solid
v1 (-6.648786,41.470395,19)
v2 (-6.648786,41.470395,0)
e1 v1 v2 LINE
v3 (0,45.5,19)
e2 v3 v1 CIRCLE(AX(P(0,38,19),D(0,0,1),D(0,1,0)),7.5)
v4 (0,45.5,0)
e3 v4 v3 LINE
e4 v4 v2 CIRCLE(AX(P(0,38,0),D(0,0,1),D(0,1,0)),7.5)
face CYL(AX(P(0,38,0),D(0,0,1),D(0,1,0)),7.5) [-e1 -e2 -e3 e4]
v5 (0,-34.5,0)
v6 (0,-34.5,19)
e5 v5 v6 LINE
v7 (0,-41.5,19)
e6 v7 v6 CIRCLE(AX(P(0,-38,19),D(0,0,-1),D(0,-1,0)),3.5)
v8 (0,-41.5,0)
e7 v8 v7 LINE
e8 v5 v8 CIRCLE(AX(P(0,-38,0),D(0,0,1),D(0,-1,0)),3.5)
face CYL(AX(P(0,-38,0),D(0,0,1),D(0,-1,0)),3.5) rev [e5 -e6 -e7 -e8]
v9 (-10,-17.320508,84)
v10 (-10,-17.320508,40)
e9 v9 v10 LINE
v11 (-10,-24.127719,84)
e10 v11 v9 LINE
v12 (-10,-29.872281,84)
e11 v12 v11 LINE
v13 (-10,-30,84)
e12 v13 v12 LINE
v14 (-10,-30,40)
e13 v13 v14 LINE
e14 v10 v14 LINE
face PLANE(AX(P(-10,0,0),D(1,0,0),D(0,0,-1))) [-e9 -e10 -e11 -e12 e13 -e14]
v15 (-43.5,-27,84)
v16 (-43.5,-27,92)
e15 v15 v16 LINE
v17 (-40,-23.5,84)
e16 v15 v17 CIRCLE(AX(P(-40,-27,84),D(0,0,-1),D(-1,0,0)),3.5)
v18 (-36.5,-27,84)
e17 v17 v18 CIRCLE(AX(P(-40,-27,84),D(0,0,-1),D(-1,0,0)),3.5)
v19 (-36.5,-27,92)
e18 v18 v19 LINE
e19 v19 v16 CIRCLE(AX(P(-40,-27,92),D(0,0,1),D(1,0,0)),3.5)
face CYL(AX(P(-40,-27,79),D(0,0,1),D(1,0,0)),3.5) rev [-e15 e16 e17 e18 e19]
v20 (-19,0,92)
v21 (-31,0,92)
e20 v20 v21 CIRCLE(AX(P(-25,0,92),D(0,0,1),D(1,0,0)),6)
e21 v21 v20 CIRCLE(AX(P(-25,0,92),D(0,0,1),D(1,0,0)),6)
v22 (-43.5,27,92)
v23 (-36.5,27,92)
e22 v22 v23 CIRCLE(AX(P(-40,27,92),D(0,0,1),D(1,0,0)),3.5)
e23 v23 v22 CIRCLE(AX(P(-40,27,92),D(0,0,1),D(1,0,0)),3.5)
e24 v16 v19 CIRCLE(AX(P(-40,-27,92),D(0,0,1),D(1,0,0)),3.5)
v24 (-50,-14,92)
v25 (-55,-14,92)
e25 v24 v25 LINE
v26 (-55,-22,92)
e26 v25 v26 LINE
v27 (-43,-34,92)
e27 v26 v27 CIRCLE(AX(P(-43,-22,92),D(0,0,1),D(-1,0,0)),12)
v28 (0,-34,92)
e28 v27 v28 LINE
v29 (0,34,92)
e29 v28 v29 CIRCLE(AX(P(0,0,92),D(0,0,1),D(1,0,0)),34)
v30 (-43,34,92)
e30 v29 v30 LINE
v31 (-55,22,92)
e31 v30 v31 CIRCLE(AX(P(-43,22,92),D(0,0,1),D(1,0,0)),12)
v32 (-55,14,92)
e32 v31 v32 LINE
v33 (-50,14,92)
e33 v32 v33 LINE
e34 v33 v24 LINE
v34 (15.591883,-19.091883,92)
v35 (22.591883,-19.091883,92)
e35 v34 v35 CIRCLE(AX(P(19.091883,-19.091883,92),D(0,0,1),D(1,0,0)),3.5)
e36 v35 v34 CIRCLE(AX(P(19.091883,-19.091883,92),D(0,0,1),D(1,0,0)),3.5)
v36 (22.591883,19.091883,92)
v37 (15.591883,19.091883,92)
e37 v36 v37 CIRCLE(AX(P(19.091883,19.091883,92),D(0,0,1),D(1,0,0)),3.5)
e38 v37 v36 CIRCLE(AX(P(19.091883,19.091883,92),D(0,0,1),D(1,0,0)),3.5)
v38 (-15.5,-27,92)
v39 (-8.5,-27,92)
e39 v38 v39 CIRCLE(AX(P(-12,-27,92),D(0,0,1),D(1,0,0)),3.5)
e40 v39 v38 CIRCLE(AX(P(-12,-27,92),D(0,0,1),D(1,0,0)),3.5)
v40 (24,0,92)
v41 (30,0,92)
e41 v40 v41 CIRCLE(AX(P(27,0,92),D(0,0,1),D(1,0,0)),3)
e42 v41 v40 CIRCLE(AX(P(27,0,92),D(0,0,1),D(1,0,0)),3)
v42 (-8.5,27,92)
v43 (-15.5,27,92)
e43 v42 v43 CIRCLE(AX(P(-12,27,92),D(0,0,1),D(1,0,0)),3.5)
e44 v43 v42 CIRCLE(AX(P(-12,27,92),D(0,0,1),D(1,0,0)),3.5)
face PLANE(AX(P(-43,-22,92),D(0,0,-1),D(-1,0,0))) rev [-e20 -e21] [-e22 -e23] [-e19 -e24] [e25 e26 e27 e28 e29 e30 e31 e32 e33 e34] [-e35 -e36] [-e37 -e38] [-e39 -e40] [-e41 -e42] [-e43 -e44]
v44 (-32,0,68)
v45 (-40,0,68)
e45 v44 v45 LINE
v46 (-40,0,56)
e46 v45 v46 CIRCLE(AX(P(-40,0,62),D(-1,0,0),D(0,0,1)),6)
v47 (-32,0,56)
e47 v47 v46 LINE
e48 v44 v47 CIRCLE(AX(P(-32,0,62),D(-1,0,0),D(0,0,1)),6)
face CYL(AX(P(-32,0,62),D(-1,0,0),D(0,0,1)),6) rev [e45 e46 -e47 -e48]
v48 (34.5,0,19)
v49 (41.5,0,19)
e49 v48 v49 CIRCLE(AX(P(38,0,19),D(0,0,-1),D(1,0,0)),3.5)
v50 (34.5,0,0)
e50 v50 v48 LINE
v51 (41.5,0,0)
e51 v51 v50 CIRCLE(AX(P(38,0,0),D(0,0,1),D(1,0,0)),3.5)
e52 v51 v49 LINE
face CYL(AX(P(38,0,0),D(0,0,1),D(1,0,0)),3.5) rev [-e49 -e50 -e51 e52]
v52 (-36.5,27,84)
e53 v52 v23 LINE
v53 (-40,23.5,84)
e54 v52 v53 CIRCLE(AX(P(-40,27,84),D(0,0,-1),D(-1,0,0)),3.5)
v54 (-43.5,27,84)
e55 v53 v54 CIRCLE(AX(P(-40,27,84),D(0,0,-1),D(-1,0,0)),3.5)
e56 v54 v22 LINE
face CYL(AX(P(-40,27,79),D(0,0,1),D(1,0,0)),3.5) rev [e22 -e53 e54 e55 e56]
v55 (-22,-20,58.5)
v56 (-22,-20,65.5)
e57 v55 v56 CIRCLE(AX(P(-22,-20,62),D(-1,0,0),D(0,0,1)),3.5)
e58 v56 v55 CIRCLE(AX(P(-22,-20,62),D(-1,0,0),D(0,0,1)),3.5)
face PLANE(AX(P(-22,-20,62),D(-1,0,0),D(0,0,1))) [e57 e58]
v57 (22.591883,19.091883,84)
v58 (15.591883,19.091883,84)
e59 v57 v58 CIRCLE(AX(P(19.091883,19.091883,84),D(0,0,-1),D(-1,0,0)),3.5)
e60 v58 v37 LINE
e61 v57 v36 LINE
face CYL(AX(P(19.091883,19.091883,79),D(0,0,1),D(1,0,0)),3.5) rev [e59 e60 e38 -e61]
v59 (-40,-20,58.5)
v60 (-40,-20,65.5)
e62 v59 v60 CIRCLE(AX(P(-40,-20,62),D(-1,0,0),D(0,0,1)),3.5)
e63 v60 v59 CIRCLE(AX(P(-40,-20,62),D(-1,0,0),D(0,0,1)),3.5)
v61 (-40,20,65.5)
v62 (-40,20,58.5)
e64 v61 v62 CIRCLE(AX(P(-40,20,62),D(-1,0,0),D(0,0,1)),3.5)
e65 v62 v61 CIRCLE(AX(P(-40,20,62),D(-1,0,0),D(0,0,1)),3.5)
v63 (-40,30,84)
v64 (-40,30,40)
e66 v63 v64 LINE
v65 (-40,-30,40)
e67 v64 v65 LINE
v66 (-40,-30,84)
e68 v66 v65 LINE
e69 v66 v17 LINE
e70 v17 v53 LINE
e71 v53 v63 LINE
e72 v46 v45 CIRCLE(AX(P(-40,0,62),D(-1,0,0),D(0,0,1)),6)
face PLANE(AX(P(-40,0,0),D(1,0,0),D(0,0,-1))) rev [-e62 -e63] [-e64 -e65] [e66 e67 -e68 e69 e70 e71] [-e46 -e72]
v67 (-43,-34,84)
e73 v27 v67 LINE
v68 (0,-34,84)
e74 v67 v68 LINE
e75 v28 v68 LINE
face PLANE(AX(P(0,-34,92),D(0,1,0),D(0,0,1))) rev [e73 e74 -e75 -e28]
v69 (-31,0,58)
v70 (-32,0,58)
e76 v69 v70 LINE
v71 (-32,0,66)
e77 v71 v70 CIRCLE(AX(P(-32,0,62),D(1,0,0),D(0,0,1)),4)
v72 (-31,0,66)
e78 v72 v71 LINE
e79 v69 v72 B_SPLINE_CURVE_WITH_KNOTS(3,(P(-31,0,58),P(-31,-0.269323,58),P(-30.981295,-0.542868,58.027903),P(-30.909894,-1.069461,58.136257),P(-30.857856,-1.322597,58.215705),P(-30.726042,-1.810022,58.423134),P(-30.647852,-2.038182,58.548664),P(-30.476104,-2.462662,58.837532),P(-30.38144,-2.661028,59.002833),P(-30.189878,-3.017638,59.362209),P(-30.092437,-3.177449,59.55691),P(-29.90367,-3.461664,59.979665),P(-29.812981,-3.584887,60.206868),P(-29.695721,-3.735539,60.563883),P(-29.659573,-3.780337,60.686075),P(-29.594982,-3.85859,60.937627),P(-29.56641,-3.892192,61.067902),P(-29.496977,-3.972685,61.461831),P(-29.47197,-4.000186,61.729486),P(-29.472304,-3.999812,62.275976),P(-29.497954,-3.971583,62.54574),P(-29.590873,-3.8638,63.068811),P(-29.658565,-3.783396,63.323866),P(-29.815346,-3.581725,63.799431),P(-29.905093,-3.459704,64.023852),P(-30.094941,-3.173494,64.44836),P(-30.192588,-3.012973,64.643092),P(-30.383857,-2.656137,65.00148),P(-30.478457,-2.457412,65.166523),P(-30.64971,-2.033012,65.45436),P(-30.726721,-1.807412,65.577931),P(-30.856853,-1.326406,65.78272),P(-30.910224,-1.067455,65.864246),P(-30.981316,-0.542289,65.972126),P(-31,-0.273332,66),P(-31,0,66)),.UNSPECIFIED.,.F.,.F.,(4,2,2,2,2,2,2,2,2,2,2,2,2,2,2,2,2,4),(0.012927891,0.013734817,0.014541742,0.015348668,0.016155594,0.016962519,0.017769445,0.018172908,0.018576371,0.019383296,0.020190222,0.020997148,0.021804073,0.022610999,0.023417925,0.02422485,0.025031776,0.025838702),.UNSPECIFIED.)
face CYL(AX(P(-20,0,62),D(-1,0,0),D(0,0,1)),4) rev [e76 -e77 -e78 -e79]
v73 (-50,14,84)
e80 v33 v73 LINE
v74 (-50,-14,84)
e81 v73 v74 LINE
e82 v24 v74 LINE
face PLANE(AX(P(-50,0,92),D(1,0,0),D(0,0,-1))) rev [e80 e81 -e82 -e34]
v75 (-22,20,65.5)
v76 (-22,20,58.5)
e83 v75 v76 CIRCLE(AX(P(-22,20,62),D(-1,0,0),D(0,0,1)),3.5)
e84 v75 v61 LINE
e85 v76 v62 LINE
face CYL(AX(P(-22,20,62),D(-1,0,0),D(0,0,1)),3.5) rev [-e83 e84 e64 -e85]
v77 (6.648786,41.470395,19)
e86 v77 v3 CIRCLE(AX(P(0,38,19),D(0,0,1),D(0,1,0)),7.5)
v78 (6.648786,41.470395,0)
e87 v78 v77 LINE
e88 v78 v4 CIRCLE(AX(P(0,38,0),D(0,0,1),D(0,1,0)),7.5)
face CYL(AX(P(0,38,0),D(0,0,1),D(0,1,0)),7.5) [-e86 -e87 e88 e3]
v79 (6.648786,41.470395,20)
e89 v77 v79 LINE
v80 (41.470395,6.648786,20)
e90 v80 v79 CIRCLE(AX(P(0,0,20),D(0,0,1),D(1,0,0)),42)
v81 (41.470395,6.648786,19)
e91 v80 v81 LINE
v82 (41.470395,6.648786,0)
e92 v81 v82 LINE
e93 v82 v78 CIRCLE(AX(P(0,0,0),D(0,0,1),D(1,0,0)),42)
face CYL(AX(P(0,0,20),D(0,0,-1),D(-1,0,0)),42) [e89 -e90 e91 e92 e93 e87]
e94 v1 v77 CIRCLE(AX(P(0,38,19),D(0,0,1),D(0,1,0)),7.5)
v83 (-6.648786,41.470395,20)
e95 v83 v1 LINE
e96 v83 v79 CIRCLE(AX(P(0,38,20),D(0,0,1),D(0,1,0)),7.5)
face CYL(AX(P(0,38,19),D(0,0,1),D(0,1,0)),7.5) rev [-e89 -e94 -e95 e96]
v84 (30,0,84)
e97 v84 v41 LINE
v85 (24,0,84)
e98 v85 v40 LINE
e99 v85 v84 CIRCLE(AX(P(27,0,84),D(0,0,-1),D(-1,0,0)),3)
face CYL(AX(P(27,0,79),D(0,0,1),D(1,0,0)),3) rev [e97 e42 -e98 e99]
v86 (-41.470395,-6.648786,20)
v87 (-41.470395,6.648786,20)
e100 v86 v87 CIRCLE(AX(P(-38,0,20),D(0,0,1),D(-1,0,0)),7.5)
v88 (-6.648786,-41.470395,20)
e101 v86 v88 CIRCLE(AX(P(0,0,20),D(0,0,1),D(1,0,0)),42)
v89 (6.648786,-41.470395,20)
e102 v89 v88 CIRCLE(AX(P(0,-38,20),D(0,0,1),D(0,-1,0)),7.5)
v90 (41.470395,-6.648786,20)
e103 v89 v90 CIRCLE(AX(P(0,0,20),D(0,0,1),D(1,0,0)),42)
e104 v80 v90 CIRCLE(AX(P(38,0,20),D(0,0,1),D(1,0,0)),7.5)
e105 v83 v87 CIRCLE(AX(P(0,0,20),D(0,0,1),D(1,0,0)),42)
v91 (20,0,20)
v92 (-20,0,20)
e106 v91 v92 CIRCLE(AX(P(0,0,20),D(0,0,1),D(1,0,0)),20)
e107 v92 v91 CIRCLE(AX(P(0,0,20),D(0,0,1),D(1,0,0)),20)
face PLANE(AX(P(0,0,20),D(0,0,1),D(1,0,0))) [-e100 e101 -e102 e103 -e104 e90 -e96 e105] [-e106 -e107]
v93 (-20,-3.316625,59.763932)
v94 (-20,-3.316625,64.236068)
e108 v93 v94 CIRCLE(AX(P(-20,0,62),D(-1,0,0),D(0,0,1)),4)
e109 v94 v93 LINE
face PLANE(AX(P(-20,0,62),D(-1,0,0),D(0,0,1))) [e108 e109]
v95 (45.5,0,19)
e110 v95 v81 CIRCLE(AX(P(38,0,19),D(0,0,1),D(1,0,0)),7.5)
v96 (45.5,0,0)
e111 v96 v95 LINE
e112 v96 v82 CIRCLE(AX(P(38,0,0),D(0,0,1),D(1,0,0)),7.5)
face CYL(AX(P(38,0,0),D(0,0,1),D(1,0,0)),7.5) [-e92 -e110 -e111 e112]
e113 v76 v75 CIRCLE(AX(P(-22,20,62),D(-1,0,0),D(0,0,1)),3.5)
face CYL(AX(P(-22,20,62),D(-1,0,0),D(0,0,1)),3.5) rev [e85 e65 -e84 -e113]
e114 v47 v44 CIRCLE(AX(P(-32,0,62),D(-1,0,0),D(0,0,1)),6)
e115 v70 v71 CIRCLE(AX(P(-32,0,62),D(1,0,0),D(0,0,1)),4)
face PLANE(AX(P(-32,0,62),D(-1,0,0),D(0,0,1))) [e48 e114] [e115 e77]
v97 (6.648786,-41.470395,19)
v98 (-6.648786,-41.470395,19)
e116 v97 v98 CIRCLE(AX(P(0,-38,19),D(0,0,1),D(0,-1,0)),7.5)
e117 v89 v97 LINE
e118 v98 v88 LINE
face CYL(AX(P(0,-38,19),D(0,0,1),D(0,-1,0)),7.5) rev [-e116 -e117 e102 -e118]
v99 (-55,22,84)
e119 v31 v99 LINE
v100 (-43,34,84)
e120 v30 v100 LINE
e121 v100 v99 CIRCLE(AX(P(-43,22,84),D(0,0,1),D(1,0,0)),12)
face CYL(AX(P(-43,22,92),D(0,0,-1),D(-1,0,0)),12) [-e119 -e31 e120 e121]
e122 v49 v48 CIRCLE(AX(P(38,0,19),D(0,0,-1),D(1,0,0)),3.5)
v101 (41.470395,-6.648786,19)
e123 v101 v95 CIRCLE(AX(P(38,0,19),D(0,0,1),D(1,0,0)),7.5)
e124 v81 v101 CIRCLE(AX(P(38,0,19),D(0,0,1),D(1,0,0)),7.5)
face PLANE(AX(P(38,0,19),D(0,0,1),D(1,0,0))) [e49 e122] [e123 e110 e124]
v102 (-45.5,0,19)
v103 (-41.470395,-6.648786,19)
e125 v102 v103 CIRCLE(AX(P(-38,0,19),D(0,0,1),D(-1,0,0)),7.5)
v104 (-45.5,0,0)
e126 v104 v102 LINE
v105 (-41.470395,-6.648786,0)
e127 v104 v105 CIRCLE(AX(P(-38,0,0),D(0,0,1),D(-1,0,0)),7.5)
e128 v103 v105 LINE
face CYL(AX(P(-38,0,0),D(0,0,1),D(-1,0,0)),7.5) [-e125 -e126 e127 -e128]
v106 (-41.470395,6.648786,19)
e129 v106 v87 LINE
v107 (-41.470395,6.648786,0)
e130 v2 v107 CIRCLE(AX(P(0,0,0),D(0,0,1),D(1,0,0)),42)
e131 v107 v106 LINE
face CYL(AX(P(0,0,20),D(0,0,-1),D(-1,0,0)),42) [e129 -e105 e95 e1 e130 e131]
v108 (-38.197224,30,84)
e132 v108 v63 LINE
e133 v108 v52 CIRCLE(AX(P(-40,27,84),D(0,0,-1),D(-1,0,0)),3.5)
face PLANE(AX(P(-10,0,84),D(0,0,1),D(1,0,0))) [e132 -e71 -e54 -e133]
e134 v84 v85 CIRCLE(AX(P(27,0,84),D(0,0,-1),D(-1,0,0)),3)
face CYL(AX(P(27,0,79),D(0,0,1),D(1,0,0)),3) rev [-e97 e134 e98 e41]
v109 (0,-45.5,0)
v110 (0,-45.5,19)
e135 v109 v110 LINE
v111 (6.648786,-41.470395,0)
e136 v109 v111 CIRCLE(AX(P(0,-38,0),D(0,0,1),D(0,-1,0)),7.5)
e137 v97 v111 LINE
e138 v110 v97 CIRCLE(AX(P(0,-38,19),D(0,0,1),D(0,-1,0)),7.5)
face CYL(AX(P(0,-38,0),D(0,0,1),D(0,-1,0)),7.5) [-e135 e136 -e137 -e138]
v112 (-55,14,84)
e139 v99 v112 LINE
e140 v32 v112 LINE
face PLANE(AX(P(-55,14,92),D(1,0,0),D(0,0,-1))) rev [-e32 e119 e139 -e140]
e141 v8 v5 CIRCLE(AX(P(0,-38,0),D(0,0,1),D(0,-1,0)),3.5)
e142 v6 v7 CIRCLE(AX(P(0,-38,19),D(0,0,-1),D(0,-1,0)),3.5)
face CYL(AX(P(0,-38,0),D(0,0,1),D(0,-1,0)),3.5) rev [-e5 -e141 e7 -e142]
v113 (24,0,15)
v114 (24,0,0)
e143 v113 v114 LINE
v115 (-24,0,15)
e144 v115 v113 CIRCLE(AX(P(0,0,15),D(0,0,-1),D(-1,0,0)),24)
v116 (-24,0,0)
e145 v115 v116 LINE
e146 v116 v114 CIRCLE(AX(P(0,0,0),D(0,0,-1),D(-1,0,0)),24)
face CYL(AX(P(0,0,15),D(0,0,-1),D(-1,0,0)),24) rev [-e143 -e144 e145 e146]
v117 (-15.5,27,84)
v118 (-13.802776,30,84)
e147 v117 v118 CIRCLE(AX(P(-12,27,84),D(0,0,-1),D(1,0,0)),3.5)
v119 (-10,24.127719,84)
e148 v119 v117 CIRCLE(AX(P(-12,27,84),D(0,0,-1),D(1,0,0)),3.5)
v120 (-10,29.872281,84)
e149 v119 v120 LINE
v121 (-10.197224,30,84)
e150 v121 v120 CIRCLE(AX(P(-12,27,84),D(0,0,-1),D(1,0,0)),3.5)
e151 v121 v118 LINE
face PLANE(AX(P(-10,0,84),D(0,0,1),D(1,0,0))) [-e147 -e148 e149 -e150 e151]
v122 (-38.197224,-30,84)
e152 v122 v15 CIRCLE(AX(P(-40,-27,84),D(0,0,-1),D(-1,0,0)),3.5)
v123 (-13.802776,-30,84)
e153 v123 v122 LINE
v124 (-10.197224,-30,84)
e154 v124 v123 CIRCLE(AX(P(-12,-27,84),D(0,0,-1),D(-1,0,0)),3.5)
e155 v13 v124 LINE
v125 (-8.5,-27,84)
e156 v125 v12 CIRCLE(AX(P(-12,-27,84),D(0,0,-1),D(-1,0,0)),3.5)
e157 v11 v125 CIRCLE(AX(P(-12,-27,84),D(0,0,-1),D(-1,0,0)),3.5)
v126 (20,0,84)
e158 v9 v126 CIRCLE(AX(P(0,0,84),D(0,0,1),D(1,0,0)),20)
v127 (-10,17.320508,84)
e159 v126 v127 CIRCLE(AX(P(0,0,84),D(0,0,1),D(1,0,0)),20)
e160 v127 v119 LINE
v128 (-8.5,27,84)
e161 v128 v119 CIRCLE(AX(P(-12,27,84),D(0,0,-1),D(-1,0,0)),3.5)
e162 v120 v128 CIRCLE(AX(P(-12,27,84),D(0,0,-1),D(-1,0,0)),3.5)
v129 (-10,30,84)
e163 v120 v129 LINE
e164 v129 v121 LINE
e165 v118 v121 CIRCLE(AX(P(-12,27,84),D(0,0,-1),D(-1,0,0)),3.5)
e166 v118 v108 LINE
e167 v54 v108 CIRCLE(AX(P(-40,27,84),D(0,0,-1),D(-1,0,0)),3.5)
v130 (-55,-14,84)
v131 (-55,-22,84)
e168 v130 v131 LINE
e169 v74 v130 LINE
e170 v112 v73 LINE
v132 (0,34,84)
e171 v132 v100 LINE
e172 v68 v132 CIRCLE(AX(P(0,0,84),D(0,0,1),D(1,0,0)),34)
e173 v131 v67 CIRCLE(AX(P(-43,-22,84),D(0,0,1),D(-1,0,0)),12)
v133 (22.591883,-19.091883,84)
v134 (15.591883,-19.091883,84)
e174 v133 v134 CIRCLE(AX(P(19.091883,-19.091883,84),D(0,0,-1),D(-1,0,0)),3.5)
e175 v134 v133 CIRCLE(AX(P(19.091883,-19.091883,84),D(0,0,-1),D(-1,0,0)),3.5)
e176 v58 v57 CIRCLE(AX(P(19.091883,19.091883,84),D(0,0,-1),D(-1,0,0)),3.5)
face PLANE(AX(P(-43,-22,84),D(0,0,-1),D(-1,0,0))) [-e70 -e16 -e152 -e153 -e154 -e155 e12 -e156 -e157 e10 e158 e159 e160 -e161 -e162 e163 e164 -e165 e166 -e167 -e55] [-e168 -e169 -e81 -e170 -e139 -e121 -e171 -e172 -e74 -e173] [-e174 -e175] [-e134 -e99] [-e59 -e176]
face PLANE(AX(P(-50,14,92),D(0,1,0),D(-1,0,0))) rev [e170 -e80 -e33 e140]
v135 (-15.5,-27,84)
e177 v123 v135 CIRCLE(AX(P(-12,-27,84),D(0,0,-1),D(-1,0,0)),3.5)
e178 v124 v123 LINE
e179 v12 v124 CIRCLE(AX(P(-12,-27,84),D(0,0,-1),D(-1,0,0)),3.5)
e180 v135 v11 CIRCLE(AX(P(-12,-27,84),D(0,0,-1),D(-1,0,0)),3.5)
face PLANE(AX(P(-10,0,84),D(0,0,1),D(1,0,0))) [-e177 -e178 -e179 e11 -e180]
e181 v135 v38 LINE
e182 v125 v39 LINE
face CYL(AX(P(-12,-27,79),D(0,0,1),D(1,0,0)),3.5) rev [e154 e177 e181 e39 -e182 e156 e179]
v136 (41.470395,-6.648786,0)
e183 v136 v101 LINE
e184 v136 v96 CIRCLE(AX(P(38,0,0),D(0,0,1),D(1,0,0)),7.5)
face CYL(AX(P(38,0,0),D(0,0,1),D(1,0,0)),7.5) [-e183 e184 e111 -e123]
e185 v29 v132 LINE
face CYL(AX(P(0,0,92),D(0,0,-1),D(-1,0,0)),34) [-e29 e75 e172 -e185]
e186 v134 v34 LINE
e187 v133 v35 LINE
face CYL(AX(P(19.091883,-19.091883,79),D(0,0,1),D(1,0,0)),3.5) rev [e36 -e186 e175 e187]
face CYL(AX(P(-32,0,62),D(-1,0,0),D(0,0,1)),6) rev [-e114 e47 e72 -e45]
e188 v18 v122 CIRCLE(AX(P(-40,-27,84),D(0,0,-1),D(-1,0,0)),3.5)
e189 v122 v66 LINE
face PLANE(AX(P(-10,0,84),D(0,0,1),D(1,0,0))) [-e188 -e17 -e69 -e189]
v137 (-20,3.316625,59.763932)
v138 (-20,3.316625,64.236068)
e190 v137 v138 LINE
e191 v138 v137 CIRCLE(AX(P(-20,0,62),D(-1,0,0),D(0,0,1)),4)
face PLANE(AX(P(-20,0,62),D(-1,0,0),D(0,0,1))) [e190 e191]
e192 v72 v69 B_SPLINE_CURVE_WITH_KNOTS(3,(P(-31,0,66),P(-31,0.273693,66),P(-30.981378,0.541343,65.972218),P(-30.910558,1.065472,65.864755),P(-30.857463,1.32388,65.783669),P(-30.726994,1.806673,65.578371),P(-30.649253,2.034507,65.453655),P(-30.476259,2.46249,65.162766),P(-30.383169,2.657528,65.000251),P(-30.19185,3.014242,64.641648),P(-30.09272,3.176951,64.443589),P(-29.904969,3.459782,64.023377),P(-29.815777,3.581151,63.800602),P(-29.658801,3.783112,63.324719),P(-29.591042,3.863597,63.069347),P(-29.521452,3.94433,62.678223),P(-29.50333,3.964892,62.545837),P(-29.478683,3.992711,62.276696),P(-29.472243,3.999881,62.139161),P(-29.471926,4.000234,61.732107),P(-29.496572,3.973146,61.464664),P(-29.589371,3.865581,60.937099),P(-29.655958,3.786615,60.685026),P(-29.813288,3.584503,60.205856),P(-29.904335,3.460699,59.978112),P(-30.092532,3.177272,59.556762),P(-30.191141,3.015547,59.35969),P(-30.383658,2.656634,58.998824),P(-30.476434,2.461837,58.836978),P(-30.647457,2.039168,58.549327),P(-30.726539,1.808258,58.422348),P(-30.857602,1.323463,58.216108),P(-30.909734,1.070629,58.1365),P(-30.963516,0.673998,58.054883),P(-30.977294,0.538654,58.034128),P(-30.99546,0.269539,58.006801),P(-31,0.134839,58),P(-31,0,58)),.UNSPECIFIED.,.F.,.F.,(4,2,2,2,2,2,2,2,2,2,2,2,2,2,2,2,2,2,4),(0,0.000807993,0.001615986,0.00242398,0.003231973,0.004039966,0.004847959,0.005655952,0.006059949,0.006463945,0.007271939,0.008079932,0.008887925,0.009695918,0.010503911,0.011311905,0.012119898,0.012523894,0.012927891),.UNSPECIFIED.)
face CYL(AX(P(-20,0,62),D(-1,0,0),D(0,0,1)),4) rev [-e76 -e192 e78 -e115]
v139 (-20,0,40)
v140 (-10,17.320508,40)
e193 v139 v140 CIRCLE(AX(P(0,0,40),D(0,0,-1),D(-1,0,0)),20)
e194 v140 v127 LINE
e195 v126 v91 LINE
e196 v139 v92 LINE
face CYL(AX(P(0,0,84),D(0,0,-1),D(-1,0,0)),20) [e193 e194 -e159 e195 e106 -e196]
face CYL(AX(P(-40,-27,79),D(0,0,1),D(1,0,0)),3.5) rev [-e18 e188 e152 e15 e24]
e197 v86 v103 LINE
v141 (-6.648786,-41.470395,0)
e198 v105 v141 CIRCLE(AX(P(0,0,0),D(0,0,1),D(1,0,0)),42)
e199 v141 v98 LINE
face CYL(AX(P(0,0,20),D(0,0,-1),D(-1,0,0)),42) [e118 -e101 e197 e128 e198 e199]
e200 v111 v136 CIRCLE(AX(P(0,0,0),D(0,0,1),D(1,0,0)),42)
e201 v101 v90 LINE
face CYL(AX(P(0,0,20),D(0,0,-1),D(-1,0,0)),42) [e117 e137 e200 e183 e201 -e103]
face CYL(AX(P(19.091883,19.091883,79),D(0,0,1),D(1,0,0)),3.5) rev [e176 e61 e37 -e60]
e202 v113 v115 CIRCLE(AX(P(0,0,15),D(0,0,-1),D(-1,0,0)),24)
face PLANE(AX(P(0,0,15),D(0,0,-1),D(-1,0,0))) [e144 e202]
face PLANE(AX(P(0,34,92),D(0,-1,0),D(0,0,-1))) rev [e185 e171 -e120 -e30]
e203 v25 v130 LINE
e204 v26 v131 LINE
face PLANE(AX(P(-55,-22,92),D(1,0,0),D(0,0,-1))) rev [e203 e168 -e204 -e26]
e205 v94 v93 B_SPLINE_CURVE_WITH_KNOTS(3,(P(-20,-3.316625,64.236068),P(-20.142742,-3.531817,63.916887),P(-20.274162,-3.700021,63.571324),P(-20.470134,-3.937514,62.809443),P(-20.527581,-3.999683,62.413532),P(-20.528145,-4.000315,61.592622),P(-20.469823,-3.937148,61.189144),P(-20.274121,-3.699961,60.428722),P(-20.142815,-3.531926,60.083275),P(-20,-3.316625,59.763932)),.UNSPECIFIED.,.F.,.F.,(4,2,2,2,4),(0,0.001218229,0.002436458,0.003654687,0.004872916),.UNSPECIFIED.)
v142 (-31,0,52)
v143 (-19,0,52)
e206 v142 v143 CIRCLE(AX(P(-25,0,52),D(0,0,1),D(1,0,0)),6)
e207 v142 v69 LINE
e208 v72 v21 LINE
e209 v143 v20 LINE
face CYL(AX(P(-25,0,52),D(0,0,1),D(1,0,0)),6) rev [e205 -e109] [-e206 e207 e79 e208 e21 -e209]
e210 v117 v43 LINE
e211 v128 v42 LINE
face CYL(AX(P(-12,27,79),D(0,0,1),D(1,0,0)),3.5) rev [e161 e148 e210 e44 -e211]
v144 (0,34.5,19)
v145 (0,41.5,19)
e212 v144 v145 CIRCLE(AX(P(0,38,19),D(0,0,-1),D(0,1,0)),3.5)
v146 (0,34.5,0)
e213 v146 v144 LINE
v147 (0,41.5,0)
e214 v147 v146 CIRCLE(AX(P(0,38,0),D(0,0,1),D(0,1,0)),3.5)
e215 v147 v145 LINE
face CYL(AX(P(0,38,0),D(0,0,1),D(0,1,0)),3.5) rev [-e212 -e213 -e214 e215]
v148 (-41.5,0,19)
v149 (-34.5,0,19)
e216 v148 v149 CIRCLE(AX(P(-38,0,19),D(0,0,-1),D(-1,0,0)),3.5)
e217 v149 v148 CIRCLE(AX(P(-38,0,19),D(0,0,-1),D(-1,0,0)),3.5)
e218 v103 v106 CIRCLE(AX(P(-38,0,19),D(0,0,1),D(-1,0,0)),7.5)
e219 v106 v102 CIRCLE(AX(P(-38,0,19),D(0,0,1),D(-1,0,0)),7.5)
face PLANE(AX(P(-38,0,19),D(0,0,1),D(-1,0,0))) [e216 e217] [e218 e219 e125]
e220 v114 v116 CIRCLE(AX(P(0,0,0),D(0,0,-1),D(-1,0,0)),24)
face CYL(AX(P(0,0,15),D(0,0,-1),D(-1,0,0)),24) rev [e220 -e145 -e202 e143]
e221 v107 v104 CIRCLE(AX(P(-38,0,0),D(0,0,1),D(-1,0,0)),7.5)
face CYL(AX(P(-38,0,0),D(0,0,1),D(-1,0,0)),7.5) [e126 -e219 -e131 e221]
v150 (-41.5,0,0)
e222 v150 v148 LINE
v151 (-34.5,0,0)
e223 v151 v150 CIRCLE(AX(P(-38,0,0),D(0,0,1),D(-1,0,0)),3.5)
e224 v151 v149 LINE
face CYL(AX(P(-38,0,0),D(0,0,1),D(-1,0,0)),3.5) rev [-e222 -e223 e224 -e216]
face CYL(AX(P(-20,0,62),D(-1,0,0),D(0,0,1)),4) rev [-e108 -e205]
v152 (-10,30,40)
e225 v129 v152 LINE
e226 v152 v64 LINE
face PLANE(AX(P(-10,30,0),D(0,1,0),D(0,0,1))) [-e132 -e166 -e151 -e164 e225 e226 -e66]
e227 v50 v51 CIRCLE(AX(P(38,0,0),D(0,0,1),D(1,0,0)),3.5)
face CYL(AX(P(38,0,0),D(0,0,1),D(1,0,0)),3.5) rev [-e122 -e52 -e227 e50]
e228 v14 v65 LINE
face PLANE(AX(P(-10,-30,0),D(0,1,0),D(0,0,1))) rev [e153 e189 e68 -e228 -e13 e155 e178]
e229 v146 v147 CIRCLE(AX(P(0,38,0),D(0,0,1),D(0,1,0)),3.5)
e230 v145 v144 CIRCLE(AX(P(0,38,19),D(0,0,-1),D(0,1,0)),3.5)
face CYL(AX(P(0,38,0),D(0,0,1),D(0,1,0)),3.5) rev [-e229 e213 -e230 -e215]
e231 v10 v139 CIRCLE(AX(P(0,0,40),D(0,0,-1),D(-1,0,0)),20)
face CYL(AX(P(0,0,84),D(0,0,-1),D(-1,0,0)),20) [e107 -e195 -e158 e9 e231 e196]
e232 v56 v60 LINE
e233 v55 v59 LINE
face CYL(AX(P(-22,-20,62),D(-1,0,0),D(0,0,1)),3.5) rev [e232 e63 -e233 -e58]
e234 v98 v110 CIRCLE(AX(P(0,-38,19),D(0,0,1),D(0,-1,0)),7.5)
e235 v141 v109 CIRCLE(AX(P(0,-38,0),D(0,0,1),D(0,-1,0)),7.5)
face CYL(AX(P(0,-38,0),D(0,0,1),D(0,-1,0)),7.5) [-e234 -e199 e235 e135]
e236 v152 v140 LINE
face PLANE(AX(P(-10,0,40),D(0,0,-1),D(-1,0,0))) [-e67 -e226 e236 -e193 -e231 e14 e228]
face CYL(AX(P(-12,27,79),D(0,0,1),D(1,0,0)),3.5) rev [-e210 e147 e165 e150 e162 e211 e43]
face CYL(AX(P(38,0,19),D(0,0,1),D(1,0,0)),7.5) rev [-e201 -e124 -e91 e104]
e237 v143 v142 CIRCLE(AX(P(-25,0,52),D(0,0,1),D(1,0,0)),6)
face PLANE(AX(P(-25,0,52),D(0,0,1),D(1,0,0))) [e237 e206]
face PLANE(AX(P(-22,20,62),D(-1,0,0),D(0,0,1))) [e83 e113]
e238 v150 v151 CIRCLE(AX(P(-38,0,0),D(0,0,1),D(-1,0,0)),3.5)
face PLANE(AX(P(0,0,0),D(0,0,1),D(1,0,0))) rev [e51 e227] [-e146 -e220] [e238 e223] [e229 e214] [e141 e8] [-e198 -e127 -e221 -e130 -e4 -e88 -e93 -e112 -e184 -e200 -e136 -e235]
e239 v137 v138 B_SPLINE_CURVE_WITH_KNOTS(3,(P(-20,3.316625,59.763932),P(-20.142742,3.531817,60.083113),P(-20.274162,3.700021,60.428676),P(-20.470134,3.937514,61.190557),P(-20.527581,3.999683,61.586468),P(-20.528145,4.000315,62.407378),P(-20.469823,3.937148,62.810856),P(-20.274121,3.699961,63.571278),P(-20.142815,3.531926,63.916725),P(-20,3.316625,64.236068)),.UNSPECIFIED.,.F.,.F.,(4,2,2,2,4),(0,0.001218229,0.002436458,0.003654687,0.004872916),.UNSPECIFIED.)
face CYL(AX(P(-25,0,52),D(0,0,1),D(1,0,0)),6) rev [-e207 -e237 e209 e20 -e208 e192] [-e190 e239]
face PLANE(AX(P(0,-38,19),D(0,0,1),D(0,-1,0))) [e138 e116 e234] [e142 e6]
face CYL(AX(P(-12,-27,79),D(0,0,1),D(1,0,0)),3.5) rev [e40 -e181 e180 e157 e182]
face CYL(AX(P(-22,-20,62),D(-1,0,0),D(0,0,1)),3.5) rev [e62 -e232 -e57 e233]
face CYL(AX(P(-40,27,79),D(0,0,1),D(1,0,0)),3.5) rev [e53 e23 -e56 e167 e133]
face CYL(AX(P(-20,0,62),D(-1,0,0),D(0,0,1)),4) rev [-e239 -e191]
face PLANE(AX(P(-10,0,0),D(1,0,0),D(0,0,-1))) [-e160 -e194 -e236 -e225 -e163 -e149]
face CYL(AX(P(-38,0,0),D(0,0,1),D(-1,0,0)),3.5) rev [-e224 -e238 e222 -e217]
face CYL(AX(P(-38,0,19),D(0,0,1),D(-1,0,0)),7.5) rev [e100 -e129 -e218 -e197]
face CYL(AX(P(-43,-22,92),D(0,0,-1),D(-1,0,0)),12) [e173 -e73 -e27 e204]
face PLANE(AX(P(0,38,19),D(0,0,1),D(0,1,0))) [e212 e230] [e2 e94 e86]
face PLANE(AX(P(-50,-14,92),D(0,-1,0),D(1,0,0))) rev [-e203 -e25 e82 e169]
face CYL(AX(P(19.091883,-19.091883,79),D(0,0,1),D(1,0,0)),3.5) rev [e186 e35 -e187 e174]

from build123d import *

# Parameters (mm, degrees)
REAR_FLANGE_SKETCH_84_R         = 42
REAR_FLANGE_84_DEPTH            = 20
BODY_CYLINDER_SKETCH_40_R       = 20
BODY_CYLINDER_40_DEPTH          = 64
FRONT_PLATE_DEPTH               = 8
FRONT_PLATE_SIDE_NOTCH_SKETCH_R = 2.5
FRONT_PLATE_SIDE_NOTCH_DEPTH    = 16
NOTCH_HOLE_SKETCH_6_R           = 3
NOTCH_HOLE_6_DEPTH              = 13
FRONT_PLATE_HOLES_SKETCH_R      = 3.5
FRONT_PLATE_HOLES_7_DEPTH       = 13
TOP_BLOCK_DEPTH                 = 30
FRONT_CENTER_BORE_SKETCH_R      = 6
FRONT_CENTER_BORE_DEPTH         = 40
TOP_BLOCK_POCKET_SKETCH_R       = 4
TOP_BLOCK_POCKET_DEPTH          = 20
TOP_BLOCK_HOLE_SKETCH_12_R      = 6
TOP_BLOCK_HOLE_12_DEPTH         = 8
TOP_BLOCK_SLOT_SKETCH_R         = 3.5
TOP_BLOCK_SLOT_DEPTH            = 18
REAR_HUB_SKETCH_40_R            = 20
REAR_HUB_40_DEPTH               = 11
FLANGE_PROFILE_TRIM_SKETCH_R    = 3.5
FLANGE_PROFILE_TRIM_DEPTH       = 100.864908824
FLANGE_LUG_SKETCH_15_R          = 7.5
FLANGE_LUG_15_DEPTH             = 20
LUG_HOLE_SKETCH_7_R             = 3.5
LUG_HOLE_7_DEPTH                = 100.864908824
LUG_RECESS_SKETCH_R             = 7.5
LUG_RECESS_1MM_DEPTH            = 1
REAR_COUNTERBORE_SKETCH_48_R    = 24
REAR_COUNTERBORE_48_DEPTH       = 15
FLANGE_LUG_PATTERN_4X_COUNT     = 4


with BuildPart() as part:
    # Rear Flange Sketch Ø84 → Rear Flange Ø84 (new body)
    with BuildSketch(Plane.XY):
        Circle(REAR_FLANGE_SKETCH_84_R)
    extrude(amount=REAR_FLANGE_84_DEPTH)

    # Body Cylinder Sketch Ø40 → Body Cylinder Ø40 (add)
    with BuildSketch(Plane.XY.offset(20)):
        Circle(BODY_CYLINDER_SKETCH_40_R)
    extrude(amount=BODY_CYLINDER_40_DEPTH)

    # Front Plate Sketch → Front Plate (add)
    with BuildSketch(Plane.XY.offset(84)):
        with BuildLine():
            Line((0, 34), (-43, 34))
            ThreePointArc((-43, 34), (-51.485281374, 30.485281374), (-55, 22))
            Line((-55, 22), (-55, 14))
            Line((-55, 14), (-50, 14))
            Line((-50, 14), (-50, 0))
            Line((-50, 0), (-50, -14))
            Line((-50, -14), (-55, -14))
            Line((-55, -14), (-55, -22))
            ThreePointArc((-55, -22), (-51.485281374, -30.485281374), (-43, -34))
            Line((-43, -34), (0, -34))
            ThreePointArc((0, -34), (34, 0), (0, 34))
        make_face()
    extrude(amount=FRONT_PLATE_DEPTH)

    # Front Plate Side Notch Sketch → Front Plate Side Notch (cut)
    with BuildSketch(Plane.XY.offset(92)):
        with Locations((27, 0)):
            Circle(FRONT_PLATE_SIDE_NOTCH_SKETCH_R)
    extrude(amount=-FRONT_PLATE_SIDE_NOTCH_DEPTH, mode=Mode.SUBTRACT)

    # Notch Hole Sketch Ø6 → Notch Hole Ø6 (cut)
    with BuildSketch(Plane.XY.offset(92)):
        with Locations((27, 0)):
            Circle(NOTCH_HOLE_SKETCH_6_R)
    extrude(amount=-NOTCH_HOLE_6_DEPTH, mode=Mode.SUBTRACT)

    # Front Plate Holes Sketch → Front Plate Holes Ø7 (cut)
    with BuildSketch(Plane.XY.offset(92)):
        with Locations((19.091883092, 19.091883092)):
            Circle(FRONT_PLATE_HOLES_SKETCH_R)
        with Locations((19.091883092, -19.091883092)):
            Circle(FRONT_PLATE_HOLES_SKETCH_R)
        with Locations((-12, 27)):
            Circle(FRONT_PLATE_HOLES_SKETCH_R)
        with Locations((-40, 27)):
            Circle(FRONT_PLATE_HOLES_SKETCH_R)
        with Locations((-12, -27)):
            Circle(FRONT_PLATE_HOLES_SKETCH_R)
        with Locations((-40, -27)):
            Circle(FRONT_PLATE_HOLES_SKETCH_R)
    extrude(amount=-FRONT_PLATE_HOLES_7_DEPTH, mode=Mode.SUBTRACT)

    # Top Block Sketch → Top Block (add)
    with BuildSketch(Plane(origin=(-40, 0, 0), x_dir=(0, 0, -1), z_dir=(1, 0, 0))):
        Polygon((-84, 30), (-84, 0), (-84, -30), (-40, -30), (-40, 0), (-40, 30), align=None)
    extrude(amount=TOP_BLOCK_DEPTH)

    # Front Center Bore Sketch → Front Center Bore (cut)
    with BuildSketch(Plane.XY.offset(92)):
        with Locations((-25, 0)):
            Circle(FRONT_CENTER_BORE_SKETCH_R)
    extrude(amount=-FRONT_CENTER_BORE_DEPTH, mode=Mode.SUBTRACT)

    # Top Block Pocket Sketch → Top Block Pocket (cut)
    with BuildSketch(Plane.ZY.offset(40)):
        with Locations((62, 0)):
            Circle(TOP_BLOCK_POCKET_SKETCH_R)
    extrude(amount=-TOP_BLOCK_POCKET_DEPTH, mode=Mode.SUBTRACT)

    # Top Block Hole Sketch Ø12 → Top Block Hole Ø12 (cut)
    with BuildSketch(Plane.ZY.offset(40)):
        with Locations((62, 0)):
            Circle(TOP_BLOCK_HOLE_SKETCH_12_R)
    extrude(amount=-TOP_BLOCK_HOLE_12_DEPTH, mode=Mode.SUBTRACT)

    # Top Block Slot Sketch → Top Block Slot (cut)
    with BuildSketch(Plane.ZY.offset(40)):
        with Locations((62, 20)):
            Circle(TOP_BLOCK_SLOT_SKETCH_R)
        with Locations((62, -20)):
            Circle(TOP_BLOCK_SLOT_SKETCH_R)
    extrude(amount=-TOP_BLOCK_SLOT_DEPTH, mode=Mode.SUBTRACT)

    # Rear Hub Sketch Ø40 → Rear Hub Ø40 (add)
    with BuildSketch(Plane.XY.offset(8)):
        with Locations(Location((0, 0, 0), (0, 0, 240))):
            Circle(REAR_HUB_SKETCH_40_R)
    extrude(amount=REAR_HUB_40_DEPTH)

    # Flange Profile Trim Sketch → Flange Profile Trim (cut, through all)
    with BuildSketch(Plane.XY.offset(20)):
        with Locations((38, 0)):
            Circle(FLANGE_PROFILE_TRIM_SKETCH_R)
    extrude(amount=-FLANGE_PROFILE_TRIM_DEPTH, mode=Mode.SUBTRACT)

    # Flange Lug Sketch Ø15 → Flange Lug Ø15 (add, through all)
    with BuildSketch(Plane.XY.offset(20)):
        with Locations((38, 0)):
            Circle(FLANGE_LUG_SKETCH_15_R)
    flange_lug_15 = extrude(amount=-FLANGE_LUG_15_DEPTH)

    # Lug Hole Sketch Ø7 → Lug Hole Ø7 (cut, through all)
    with BuildSketch(Plane.XY.offset(20)):
        with Locations((38, 0)):
            Circle(LUG_HOLE_SKETCH_7_R)
    lug_hole_7 = extrude(amount=-LUG_HOLE_7_DEPTH, mode=Mode.SUBTRACT)

    # Lug Recess Sketch → Lug Recess 1mm (cut)
    with BuildSketch(Plane.XY.offset(20)):
        with Locations((38, 0)):
            Circle(LUG_RECESS_SKETCH_R)
    lug_recess_1mm = extrude(amount=-LUG_RECESS_1MM_DEPTH, mode=Mode.SUBTRACT)

    # Rear Counterbore Sketch Ø48 → Rear Counterbore Ø48 (cut)
    with BuildSketch(Plane(origin=(0, 0, 0), x_dir=(-1, 0, 0), z_dir=(0, 0, -1))):
        Circle(REAR_COUNTERBORE_SKETCH_48_R)
    extrude(amount=-REAR_COUNTERBORE_48_DEPTH, mode=Mode.SUBTRACT)

    # Flange Lug Pattern 4x: Flange Lug Ø15, Lug Hole Ø7, Lug Recess 1mm ×4 about axis
    flange_lug_pattern_4x_axis = Axis((0, 0, 0), (0, 0, 1))
    add([flange_lug_15.rotate(flange_lug_pattern_4x_axis, i * 360 / FLANGE_LUG_PATTERN_4X_COUNT) for i in range(1, FLANGE_LUG_PATTERN_4X_COUNT)])
    add([lug_hole_7.rotate(flange_lug_pattern_4x_axis, i * 360 / FLANGE_LUG_PATTERN_4X_COUNT) for i in range(1, FLANGE_LUG_PATTERN_4X_COUNT)], mode=Mode.SUBTRACT)
    add([lug_recess_1mm.rotate(flange_lug_pattern_4x_axis, i * 360 / FLANGE_LUG_PATTERN_4X_COUNT) for i in range(1, FLANGE_LUG_PATTERN_4X_COUNT)], mode=Mode.SUBTRACT)


solid = part.part
